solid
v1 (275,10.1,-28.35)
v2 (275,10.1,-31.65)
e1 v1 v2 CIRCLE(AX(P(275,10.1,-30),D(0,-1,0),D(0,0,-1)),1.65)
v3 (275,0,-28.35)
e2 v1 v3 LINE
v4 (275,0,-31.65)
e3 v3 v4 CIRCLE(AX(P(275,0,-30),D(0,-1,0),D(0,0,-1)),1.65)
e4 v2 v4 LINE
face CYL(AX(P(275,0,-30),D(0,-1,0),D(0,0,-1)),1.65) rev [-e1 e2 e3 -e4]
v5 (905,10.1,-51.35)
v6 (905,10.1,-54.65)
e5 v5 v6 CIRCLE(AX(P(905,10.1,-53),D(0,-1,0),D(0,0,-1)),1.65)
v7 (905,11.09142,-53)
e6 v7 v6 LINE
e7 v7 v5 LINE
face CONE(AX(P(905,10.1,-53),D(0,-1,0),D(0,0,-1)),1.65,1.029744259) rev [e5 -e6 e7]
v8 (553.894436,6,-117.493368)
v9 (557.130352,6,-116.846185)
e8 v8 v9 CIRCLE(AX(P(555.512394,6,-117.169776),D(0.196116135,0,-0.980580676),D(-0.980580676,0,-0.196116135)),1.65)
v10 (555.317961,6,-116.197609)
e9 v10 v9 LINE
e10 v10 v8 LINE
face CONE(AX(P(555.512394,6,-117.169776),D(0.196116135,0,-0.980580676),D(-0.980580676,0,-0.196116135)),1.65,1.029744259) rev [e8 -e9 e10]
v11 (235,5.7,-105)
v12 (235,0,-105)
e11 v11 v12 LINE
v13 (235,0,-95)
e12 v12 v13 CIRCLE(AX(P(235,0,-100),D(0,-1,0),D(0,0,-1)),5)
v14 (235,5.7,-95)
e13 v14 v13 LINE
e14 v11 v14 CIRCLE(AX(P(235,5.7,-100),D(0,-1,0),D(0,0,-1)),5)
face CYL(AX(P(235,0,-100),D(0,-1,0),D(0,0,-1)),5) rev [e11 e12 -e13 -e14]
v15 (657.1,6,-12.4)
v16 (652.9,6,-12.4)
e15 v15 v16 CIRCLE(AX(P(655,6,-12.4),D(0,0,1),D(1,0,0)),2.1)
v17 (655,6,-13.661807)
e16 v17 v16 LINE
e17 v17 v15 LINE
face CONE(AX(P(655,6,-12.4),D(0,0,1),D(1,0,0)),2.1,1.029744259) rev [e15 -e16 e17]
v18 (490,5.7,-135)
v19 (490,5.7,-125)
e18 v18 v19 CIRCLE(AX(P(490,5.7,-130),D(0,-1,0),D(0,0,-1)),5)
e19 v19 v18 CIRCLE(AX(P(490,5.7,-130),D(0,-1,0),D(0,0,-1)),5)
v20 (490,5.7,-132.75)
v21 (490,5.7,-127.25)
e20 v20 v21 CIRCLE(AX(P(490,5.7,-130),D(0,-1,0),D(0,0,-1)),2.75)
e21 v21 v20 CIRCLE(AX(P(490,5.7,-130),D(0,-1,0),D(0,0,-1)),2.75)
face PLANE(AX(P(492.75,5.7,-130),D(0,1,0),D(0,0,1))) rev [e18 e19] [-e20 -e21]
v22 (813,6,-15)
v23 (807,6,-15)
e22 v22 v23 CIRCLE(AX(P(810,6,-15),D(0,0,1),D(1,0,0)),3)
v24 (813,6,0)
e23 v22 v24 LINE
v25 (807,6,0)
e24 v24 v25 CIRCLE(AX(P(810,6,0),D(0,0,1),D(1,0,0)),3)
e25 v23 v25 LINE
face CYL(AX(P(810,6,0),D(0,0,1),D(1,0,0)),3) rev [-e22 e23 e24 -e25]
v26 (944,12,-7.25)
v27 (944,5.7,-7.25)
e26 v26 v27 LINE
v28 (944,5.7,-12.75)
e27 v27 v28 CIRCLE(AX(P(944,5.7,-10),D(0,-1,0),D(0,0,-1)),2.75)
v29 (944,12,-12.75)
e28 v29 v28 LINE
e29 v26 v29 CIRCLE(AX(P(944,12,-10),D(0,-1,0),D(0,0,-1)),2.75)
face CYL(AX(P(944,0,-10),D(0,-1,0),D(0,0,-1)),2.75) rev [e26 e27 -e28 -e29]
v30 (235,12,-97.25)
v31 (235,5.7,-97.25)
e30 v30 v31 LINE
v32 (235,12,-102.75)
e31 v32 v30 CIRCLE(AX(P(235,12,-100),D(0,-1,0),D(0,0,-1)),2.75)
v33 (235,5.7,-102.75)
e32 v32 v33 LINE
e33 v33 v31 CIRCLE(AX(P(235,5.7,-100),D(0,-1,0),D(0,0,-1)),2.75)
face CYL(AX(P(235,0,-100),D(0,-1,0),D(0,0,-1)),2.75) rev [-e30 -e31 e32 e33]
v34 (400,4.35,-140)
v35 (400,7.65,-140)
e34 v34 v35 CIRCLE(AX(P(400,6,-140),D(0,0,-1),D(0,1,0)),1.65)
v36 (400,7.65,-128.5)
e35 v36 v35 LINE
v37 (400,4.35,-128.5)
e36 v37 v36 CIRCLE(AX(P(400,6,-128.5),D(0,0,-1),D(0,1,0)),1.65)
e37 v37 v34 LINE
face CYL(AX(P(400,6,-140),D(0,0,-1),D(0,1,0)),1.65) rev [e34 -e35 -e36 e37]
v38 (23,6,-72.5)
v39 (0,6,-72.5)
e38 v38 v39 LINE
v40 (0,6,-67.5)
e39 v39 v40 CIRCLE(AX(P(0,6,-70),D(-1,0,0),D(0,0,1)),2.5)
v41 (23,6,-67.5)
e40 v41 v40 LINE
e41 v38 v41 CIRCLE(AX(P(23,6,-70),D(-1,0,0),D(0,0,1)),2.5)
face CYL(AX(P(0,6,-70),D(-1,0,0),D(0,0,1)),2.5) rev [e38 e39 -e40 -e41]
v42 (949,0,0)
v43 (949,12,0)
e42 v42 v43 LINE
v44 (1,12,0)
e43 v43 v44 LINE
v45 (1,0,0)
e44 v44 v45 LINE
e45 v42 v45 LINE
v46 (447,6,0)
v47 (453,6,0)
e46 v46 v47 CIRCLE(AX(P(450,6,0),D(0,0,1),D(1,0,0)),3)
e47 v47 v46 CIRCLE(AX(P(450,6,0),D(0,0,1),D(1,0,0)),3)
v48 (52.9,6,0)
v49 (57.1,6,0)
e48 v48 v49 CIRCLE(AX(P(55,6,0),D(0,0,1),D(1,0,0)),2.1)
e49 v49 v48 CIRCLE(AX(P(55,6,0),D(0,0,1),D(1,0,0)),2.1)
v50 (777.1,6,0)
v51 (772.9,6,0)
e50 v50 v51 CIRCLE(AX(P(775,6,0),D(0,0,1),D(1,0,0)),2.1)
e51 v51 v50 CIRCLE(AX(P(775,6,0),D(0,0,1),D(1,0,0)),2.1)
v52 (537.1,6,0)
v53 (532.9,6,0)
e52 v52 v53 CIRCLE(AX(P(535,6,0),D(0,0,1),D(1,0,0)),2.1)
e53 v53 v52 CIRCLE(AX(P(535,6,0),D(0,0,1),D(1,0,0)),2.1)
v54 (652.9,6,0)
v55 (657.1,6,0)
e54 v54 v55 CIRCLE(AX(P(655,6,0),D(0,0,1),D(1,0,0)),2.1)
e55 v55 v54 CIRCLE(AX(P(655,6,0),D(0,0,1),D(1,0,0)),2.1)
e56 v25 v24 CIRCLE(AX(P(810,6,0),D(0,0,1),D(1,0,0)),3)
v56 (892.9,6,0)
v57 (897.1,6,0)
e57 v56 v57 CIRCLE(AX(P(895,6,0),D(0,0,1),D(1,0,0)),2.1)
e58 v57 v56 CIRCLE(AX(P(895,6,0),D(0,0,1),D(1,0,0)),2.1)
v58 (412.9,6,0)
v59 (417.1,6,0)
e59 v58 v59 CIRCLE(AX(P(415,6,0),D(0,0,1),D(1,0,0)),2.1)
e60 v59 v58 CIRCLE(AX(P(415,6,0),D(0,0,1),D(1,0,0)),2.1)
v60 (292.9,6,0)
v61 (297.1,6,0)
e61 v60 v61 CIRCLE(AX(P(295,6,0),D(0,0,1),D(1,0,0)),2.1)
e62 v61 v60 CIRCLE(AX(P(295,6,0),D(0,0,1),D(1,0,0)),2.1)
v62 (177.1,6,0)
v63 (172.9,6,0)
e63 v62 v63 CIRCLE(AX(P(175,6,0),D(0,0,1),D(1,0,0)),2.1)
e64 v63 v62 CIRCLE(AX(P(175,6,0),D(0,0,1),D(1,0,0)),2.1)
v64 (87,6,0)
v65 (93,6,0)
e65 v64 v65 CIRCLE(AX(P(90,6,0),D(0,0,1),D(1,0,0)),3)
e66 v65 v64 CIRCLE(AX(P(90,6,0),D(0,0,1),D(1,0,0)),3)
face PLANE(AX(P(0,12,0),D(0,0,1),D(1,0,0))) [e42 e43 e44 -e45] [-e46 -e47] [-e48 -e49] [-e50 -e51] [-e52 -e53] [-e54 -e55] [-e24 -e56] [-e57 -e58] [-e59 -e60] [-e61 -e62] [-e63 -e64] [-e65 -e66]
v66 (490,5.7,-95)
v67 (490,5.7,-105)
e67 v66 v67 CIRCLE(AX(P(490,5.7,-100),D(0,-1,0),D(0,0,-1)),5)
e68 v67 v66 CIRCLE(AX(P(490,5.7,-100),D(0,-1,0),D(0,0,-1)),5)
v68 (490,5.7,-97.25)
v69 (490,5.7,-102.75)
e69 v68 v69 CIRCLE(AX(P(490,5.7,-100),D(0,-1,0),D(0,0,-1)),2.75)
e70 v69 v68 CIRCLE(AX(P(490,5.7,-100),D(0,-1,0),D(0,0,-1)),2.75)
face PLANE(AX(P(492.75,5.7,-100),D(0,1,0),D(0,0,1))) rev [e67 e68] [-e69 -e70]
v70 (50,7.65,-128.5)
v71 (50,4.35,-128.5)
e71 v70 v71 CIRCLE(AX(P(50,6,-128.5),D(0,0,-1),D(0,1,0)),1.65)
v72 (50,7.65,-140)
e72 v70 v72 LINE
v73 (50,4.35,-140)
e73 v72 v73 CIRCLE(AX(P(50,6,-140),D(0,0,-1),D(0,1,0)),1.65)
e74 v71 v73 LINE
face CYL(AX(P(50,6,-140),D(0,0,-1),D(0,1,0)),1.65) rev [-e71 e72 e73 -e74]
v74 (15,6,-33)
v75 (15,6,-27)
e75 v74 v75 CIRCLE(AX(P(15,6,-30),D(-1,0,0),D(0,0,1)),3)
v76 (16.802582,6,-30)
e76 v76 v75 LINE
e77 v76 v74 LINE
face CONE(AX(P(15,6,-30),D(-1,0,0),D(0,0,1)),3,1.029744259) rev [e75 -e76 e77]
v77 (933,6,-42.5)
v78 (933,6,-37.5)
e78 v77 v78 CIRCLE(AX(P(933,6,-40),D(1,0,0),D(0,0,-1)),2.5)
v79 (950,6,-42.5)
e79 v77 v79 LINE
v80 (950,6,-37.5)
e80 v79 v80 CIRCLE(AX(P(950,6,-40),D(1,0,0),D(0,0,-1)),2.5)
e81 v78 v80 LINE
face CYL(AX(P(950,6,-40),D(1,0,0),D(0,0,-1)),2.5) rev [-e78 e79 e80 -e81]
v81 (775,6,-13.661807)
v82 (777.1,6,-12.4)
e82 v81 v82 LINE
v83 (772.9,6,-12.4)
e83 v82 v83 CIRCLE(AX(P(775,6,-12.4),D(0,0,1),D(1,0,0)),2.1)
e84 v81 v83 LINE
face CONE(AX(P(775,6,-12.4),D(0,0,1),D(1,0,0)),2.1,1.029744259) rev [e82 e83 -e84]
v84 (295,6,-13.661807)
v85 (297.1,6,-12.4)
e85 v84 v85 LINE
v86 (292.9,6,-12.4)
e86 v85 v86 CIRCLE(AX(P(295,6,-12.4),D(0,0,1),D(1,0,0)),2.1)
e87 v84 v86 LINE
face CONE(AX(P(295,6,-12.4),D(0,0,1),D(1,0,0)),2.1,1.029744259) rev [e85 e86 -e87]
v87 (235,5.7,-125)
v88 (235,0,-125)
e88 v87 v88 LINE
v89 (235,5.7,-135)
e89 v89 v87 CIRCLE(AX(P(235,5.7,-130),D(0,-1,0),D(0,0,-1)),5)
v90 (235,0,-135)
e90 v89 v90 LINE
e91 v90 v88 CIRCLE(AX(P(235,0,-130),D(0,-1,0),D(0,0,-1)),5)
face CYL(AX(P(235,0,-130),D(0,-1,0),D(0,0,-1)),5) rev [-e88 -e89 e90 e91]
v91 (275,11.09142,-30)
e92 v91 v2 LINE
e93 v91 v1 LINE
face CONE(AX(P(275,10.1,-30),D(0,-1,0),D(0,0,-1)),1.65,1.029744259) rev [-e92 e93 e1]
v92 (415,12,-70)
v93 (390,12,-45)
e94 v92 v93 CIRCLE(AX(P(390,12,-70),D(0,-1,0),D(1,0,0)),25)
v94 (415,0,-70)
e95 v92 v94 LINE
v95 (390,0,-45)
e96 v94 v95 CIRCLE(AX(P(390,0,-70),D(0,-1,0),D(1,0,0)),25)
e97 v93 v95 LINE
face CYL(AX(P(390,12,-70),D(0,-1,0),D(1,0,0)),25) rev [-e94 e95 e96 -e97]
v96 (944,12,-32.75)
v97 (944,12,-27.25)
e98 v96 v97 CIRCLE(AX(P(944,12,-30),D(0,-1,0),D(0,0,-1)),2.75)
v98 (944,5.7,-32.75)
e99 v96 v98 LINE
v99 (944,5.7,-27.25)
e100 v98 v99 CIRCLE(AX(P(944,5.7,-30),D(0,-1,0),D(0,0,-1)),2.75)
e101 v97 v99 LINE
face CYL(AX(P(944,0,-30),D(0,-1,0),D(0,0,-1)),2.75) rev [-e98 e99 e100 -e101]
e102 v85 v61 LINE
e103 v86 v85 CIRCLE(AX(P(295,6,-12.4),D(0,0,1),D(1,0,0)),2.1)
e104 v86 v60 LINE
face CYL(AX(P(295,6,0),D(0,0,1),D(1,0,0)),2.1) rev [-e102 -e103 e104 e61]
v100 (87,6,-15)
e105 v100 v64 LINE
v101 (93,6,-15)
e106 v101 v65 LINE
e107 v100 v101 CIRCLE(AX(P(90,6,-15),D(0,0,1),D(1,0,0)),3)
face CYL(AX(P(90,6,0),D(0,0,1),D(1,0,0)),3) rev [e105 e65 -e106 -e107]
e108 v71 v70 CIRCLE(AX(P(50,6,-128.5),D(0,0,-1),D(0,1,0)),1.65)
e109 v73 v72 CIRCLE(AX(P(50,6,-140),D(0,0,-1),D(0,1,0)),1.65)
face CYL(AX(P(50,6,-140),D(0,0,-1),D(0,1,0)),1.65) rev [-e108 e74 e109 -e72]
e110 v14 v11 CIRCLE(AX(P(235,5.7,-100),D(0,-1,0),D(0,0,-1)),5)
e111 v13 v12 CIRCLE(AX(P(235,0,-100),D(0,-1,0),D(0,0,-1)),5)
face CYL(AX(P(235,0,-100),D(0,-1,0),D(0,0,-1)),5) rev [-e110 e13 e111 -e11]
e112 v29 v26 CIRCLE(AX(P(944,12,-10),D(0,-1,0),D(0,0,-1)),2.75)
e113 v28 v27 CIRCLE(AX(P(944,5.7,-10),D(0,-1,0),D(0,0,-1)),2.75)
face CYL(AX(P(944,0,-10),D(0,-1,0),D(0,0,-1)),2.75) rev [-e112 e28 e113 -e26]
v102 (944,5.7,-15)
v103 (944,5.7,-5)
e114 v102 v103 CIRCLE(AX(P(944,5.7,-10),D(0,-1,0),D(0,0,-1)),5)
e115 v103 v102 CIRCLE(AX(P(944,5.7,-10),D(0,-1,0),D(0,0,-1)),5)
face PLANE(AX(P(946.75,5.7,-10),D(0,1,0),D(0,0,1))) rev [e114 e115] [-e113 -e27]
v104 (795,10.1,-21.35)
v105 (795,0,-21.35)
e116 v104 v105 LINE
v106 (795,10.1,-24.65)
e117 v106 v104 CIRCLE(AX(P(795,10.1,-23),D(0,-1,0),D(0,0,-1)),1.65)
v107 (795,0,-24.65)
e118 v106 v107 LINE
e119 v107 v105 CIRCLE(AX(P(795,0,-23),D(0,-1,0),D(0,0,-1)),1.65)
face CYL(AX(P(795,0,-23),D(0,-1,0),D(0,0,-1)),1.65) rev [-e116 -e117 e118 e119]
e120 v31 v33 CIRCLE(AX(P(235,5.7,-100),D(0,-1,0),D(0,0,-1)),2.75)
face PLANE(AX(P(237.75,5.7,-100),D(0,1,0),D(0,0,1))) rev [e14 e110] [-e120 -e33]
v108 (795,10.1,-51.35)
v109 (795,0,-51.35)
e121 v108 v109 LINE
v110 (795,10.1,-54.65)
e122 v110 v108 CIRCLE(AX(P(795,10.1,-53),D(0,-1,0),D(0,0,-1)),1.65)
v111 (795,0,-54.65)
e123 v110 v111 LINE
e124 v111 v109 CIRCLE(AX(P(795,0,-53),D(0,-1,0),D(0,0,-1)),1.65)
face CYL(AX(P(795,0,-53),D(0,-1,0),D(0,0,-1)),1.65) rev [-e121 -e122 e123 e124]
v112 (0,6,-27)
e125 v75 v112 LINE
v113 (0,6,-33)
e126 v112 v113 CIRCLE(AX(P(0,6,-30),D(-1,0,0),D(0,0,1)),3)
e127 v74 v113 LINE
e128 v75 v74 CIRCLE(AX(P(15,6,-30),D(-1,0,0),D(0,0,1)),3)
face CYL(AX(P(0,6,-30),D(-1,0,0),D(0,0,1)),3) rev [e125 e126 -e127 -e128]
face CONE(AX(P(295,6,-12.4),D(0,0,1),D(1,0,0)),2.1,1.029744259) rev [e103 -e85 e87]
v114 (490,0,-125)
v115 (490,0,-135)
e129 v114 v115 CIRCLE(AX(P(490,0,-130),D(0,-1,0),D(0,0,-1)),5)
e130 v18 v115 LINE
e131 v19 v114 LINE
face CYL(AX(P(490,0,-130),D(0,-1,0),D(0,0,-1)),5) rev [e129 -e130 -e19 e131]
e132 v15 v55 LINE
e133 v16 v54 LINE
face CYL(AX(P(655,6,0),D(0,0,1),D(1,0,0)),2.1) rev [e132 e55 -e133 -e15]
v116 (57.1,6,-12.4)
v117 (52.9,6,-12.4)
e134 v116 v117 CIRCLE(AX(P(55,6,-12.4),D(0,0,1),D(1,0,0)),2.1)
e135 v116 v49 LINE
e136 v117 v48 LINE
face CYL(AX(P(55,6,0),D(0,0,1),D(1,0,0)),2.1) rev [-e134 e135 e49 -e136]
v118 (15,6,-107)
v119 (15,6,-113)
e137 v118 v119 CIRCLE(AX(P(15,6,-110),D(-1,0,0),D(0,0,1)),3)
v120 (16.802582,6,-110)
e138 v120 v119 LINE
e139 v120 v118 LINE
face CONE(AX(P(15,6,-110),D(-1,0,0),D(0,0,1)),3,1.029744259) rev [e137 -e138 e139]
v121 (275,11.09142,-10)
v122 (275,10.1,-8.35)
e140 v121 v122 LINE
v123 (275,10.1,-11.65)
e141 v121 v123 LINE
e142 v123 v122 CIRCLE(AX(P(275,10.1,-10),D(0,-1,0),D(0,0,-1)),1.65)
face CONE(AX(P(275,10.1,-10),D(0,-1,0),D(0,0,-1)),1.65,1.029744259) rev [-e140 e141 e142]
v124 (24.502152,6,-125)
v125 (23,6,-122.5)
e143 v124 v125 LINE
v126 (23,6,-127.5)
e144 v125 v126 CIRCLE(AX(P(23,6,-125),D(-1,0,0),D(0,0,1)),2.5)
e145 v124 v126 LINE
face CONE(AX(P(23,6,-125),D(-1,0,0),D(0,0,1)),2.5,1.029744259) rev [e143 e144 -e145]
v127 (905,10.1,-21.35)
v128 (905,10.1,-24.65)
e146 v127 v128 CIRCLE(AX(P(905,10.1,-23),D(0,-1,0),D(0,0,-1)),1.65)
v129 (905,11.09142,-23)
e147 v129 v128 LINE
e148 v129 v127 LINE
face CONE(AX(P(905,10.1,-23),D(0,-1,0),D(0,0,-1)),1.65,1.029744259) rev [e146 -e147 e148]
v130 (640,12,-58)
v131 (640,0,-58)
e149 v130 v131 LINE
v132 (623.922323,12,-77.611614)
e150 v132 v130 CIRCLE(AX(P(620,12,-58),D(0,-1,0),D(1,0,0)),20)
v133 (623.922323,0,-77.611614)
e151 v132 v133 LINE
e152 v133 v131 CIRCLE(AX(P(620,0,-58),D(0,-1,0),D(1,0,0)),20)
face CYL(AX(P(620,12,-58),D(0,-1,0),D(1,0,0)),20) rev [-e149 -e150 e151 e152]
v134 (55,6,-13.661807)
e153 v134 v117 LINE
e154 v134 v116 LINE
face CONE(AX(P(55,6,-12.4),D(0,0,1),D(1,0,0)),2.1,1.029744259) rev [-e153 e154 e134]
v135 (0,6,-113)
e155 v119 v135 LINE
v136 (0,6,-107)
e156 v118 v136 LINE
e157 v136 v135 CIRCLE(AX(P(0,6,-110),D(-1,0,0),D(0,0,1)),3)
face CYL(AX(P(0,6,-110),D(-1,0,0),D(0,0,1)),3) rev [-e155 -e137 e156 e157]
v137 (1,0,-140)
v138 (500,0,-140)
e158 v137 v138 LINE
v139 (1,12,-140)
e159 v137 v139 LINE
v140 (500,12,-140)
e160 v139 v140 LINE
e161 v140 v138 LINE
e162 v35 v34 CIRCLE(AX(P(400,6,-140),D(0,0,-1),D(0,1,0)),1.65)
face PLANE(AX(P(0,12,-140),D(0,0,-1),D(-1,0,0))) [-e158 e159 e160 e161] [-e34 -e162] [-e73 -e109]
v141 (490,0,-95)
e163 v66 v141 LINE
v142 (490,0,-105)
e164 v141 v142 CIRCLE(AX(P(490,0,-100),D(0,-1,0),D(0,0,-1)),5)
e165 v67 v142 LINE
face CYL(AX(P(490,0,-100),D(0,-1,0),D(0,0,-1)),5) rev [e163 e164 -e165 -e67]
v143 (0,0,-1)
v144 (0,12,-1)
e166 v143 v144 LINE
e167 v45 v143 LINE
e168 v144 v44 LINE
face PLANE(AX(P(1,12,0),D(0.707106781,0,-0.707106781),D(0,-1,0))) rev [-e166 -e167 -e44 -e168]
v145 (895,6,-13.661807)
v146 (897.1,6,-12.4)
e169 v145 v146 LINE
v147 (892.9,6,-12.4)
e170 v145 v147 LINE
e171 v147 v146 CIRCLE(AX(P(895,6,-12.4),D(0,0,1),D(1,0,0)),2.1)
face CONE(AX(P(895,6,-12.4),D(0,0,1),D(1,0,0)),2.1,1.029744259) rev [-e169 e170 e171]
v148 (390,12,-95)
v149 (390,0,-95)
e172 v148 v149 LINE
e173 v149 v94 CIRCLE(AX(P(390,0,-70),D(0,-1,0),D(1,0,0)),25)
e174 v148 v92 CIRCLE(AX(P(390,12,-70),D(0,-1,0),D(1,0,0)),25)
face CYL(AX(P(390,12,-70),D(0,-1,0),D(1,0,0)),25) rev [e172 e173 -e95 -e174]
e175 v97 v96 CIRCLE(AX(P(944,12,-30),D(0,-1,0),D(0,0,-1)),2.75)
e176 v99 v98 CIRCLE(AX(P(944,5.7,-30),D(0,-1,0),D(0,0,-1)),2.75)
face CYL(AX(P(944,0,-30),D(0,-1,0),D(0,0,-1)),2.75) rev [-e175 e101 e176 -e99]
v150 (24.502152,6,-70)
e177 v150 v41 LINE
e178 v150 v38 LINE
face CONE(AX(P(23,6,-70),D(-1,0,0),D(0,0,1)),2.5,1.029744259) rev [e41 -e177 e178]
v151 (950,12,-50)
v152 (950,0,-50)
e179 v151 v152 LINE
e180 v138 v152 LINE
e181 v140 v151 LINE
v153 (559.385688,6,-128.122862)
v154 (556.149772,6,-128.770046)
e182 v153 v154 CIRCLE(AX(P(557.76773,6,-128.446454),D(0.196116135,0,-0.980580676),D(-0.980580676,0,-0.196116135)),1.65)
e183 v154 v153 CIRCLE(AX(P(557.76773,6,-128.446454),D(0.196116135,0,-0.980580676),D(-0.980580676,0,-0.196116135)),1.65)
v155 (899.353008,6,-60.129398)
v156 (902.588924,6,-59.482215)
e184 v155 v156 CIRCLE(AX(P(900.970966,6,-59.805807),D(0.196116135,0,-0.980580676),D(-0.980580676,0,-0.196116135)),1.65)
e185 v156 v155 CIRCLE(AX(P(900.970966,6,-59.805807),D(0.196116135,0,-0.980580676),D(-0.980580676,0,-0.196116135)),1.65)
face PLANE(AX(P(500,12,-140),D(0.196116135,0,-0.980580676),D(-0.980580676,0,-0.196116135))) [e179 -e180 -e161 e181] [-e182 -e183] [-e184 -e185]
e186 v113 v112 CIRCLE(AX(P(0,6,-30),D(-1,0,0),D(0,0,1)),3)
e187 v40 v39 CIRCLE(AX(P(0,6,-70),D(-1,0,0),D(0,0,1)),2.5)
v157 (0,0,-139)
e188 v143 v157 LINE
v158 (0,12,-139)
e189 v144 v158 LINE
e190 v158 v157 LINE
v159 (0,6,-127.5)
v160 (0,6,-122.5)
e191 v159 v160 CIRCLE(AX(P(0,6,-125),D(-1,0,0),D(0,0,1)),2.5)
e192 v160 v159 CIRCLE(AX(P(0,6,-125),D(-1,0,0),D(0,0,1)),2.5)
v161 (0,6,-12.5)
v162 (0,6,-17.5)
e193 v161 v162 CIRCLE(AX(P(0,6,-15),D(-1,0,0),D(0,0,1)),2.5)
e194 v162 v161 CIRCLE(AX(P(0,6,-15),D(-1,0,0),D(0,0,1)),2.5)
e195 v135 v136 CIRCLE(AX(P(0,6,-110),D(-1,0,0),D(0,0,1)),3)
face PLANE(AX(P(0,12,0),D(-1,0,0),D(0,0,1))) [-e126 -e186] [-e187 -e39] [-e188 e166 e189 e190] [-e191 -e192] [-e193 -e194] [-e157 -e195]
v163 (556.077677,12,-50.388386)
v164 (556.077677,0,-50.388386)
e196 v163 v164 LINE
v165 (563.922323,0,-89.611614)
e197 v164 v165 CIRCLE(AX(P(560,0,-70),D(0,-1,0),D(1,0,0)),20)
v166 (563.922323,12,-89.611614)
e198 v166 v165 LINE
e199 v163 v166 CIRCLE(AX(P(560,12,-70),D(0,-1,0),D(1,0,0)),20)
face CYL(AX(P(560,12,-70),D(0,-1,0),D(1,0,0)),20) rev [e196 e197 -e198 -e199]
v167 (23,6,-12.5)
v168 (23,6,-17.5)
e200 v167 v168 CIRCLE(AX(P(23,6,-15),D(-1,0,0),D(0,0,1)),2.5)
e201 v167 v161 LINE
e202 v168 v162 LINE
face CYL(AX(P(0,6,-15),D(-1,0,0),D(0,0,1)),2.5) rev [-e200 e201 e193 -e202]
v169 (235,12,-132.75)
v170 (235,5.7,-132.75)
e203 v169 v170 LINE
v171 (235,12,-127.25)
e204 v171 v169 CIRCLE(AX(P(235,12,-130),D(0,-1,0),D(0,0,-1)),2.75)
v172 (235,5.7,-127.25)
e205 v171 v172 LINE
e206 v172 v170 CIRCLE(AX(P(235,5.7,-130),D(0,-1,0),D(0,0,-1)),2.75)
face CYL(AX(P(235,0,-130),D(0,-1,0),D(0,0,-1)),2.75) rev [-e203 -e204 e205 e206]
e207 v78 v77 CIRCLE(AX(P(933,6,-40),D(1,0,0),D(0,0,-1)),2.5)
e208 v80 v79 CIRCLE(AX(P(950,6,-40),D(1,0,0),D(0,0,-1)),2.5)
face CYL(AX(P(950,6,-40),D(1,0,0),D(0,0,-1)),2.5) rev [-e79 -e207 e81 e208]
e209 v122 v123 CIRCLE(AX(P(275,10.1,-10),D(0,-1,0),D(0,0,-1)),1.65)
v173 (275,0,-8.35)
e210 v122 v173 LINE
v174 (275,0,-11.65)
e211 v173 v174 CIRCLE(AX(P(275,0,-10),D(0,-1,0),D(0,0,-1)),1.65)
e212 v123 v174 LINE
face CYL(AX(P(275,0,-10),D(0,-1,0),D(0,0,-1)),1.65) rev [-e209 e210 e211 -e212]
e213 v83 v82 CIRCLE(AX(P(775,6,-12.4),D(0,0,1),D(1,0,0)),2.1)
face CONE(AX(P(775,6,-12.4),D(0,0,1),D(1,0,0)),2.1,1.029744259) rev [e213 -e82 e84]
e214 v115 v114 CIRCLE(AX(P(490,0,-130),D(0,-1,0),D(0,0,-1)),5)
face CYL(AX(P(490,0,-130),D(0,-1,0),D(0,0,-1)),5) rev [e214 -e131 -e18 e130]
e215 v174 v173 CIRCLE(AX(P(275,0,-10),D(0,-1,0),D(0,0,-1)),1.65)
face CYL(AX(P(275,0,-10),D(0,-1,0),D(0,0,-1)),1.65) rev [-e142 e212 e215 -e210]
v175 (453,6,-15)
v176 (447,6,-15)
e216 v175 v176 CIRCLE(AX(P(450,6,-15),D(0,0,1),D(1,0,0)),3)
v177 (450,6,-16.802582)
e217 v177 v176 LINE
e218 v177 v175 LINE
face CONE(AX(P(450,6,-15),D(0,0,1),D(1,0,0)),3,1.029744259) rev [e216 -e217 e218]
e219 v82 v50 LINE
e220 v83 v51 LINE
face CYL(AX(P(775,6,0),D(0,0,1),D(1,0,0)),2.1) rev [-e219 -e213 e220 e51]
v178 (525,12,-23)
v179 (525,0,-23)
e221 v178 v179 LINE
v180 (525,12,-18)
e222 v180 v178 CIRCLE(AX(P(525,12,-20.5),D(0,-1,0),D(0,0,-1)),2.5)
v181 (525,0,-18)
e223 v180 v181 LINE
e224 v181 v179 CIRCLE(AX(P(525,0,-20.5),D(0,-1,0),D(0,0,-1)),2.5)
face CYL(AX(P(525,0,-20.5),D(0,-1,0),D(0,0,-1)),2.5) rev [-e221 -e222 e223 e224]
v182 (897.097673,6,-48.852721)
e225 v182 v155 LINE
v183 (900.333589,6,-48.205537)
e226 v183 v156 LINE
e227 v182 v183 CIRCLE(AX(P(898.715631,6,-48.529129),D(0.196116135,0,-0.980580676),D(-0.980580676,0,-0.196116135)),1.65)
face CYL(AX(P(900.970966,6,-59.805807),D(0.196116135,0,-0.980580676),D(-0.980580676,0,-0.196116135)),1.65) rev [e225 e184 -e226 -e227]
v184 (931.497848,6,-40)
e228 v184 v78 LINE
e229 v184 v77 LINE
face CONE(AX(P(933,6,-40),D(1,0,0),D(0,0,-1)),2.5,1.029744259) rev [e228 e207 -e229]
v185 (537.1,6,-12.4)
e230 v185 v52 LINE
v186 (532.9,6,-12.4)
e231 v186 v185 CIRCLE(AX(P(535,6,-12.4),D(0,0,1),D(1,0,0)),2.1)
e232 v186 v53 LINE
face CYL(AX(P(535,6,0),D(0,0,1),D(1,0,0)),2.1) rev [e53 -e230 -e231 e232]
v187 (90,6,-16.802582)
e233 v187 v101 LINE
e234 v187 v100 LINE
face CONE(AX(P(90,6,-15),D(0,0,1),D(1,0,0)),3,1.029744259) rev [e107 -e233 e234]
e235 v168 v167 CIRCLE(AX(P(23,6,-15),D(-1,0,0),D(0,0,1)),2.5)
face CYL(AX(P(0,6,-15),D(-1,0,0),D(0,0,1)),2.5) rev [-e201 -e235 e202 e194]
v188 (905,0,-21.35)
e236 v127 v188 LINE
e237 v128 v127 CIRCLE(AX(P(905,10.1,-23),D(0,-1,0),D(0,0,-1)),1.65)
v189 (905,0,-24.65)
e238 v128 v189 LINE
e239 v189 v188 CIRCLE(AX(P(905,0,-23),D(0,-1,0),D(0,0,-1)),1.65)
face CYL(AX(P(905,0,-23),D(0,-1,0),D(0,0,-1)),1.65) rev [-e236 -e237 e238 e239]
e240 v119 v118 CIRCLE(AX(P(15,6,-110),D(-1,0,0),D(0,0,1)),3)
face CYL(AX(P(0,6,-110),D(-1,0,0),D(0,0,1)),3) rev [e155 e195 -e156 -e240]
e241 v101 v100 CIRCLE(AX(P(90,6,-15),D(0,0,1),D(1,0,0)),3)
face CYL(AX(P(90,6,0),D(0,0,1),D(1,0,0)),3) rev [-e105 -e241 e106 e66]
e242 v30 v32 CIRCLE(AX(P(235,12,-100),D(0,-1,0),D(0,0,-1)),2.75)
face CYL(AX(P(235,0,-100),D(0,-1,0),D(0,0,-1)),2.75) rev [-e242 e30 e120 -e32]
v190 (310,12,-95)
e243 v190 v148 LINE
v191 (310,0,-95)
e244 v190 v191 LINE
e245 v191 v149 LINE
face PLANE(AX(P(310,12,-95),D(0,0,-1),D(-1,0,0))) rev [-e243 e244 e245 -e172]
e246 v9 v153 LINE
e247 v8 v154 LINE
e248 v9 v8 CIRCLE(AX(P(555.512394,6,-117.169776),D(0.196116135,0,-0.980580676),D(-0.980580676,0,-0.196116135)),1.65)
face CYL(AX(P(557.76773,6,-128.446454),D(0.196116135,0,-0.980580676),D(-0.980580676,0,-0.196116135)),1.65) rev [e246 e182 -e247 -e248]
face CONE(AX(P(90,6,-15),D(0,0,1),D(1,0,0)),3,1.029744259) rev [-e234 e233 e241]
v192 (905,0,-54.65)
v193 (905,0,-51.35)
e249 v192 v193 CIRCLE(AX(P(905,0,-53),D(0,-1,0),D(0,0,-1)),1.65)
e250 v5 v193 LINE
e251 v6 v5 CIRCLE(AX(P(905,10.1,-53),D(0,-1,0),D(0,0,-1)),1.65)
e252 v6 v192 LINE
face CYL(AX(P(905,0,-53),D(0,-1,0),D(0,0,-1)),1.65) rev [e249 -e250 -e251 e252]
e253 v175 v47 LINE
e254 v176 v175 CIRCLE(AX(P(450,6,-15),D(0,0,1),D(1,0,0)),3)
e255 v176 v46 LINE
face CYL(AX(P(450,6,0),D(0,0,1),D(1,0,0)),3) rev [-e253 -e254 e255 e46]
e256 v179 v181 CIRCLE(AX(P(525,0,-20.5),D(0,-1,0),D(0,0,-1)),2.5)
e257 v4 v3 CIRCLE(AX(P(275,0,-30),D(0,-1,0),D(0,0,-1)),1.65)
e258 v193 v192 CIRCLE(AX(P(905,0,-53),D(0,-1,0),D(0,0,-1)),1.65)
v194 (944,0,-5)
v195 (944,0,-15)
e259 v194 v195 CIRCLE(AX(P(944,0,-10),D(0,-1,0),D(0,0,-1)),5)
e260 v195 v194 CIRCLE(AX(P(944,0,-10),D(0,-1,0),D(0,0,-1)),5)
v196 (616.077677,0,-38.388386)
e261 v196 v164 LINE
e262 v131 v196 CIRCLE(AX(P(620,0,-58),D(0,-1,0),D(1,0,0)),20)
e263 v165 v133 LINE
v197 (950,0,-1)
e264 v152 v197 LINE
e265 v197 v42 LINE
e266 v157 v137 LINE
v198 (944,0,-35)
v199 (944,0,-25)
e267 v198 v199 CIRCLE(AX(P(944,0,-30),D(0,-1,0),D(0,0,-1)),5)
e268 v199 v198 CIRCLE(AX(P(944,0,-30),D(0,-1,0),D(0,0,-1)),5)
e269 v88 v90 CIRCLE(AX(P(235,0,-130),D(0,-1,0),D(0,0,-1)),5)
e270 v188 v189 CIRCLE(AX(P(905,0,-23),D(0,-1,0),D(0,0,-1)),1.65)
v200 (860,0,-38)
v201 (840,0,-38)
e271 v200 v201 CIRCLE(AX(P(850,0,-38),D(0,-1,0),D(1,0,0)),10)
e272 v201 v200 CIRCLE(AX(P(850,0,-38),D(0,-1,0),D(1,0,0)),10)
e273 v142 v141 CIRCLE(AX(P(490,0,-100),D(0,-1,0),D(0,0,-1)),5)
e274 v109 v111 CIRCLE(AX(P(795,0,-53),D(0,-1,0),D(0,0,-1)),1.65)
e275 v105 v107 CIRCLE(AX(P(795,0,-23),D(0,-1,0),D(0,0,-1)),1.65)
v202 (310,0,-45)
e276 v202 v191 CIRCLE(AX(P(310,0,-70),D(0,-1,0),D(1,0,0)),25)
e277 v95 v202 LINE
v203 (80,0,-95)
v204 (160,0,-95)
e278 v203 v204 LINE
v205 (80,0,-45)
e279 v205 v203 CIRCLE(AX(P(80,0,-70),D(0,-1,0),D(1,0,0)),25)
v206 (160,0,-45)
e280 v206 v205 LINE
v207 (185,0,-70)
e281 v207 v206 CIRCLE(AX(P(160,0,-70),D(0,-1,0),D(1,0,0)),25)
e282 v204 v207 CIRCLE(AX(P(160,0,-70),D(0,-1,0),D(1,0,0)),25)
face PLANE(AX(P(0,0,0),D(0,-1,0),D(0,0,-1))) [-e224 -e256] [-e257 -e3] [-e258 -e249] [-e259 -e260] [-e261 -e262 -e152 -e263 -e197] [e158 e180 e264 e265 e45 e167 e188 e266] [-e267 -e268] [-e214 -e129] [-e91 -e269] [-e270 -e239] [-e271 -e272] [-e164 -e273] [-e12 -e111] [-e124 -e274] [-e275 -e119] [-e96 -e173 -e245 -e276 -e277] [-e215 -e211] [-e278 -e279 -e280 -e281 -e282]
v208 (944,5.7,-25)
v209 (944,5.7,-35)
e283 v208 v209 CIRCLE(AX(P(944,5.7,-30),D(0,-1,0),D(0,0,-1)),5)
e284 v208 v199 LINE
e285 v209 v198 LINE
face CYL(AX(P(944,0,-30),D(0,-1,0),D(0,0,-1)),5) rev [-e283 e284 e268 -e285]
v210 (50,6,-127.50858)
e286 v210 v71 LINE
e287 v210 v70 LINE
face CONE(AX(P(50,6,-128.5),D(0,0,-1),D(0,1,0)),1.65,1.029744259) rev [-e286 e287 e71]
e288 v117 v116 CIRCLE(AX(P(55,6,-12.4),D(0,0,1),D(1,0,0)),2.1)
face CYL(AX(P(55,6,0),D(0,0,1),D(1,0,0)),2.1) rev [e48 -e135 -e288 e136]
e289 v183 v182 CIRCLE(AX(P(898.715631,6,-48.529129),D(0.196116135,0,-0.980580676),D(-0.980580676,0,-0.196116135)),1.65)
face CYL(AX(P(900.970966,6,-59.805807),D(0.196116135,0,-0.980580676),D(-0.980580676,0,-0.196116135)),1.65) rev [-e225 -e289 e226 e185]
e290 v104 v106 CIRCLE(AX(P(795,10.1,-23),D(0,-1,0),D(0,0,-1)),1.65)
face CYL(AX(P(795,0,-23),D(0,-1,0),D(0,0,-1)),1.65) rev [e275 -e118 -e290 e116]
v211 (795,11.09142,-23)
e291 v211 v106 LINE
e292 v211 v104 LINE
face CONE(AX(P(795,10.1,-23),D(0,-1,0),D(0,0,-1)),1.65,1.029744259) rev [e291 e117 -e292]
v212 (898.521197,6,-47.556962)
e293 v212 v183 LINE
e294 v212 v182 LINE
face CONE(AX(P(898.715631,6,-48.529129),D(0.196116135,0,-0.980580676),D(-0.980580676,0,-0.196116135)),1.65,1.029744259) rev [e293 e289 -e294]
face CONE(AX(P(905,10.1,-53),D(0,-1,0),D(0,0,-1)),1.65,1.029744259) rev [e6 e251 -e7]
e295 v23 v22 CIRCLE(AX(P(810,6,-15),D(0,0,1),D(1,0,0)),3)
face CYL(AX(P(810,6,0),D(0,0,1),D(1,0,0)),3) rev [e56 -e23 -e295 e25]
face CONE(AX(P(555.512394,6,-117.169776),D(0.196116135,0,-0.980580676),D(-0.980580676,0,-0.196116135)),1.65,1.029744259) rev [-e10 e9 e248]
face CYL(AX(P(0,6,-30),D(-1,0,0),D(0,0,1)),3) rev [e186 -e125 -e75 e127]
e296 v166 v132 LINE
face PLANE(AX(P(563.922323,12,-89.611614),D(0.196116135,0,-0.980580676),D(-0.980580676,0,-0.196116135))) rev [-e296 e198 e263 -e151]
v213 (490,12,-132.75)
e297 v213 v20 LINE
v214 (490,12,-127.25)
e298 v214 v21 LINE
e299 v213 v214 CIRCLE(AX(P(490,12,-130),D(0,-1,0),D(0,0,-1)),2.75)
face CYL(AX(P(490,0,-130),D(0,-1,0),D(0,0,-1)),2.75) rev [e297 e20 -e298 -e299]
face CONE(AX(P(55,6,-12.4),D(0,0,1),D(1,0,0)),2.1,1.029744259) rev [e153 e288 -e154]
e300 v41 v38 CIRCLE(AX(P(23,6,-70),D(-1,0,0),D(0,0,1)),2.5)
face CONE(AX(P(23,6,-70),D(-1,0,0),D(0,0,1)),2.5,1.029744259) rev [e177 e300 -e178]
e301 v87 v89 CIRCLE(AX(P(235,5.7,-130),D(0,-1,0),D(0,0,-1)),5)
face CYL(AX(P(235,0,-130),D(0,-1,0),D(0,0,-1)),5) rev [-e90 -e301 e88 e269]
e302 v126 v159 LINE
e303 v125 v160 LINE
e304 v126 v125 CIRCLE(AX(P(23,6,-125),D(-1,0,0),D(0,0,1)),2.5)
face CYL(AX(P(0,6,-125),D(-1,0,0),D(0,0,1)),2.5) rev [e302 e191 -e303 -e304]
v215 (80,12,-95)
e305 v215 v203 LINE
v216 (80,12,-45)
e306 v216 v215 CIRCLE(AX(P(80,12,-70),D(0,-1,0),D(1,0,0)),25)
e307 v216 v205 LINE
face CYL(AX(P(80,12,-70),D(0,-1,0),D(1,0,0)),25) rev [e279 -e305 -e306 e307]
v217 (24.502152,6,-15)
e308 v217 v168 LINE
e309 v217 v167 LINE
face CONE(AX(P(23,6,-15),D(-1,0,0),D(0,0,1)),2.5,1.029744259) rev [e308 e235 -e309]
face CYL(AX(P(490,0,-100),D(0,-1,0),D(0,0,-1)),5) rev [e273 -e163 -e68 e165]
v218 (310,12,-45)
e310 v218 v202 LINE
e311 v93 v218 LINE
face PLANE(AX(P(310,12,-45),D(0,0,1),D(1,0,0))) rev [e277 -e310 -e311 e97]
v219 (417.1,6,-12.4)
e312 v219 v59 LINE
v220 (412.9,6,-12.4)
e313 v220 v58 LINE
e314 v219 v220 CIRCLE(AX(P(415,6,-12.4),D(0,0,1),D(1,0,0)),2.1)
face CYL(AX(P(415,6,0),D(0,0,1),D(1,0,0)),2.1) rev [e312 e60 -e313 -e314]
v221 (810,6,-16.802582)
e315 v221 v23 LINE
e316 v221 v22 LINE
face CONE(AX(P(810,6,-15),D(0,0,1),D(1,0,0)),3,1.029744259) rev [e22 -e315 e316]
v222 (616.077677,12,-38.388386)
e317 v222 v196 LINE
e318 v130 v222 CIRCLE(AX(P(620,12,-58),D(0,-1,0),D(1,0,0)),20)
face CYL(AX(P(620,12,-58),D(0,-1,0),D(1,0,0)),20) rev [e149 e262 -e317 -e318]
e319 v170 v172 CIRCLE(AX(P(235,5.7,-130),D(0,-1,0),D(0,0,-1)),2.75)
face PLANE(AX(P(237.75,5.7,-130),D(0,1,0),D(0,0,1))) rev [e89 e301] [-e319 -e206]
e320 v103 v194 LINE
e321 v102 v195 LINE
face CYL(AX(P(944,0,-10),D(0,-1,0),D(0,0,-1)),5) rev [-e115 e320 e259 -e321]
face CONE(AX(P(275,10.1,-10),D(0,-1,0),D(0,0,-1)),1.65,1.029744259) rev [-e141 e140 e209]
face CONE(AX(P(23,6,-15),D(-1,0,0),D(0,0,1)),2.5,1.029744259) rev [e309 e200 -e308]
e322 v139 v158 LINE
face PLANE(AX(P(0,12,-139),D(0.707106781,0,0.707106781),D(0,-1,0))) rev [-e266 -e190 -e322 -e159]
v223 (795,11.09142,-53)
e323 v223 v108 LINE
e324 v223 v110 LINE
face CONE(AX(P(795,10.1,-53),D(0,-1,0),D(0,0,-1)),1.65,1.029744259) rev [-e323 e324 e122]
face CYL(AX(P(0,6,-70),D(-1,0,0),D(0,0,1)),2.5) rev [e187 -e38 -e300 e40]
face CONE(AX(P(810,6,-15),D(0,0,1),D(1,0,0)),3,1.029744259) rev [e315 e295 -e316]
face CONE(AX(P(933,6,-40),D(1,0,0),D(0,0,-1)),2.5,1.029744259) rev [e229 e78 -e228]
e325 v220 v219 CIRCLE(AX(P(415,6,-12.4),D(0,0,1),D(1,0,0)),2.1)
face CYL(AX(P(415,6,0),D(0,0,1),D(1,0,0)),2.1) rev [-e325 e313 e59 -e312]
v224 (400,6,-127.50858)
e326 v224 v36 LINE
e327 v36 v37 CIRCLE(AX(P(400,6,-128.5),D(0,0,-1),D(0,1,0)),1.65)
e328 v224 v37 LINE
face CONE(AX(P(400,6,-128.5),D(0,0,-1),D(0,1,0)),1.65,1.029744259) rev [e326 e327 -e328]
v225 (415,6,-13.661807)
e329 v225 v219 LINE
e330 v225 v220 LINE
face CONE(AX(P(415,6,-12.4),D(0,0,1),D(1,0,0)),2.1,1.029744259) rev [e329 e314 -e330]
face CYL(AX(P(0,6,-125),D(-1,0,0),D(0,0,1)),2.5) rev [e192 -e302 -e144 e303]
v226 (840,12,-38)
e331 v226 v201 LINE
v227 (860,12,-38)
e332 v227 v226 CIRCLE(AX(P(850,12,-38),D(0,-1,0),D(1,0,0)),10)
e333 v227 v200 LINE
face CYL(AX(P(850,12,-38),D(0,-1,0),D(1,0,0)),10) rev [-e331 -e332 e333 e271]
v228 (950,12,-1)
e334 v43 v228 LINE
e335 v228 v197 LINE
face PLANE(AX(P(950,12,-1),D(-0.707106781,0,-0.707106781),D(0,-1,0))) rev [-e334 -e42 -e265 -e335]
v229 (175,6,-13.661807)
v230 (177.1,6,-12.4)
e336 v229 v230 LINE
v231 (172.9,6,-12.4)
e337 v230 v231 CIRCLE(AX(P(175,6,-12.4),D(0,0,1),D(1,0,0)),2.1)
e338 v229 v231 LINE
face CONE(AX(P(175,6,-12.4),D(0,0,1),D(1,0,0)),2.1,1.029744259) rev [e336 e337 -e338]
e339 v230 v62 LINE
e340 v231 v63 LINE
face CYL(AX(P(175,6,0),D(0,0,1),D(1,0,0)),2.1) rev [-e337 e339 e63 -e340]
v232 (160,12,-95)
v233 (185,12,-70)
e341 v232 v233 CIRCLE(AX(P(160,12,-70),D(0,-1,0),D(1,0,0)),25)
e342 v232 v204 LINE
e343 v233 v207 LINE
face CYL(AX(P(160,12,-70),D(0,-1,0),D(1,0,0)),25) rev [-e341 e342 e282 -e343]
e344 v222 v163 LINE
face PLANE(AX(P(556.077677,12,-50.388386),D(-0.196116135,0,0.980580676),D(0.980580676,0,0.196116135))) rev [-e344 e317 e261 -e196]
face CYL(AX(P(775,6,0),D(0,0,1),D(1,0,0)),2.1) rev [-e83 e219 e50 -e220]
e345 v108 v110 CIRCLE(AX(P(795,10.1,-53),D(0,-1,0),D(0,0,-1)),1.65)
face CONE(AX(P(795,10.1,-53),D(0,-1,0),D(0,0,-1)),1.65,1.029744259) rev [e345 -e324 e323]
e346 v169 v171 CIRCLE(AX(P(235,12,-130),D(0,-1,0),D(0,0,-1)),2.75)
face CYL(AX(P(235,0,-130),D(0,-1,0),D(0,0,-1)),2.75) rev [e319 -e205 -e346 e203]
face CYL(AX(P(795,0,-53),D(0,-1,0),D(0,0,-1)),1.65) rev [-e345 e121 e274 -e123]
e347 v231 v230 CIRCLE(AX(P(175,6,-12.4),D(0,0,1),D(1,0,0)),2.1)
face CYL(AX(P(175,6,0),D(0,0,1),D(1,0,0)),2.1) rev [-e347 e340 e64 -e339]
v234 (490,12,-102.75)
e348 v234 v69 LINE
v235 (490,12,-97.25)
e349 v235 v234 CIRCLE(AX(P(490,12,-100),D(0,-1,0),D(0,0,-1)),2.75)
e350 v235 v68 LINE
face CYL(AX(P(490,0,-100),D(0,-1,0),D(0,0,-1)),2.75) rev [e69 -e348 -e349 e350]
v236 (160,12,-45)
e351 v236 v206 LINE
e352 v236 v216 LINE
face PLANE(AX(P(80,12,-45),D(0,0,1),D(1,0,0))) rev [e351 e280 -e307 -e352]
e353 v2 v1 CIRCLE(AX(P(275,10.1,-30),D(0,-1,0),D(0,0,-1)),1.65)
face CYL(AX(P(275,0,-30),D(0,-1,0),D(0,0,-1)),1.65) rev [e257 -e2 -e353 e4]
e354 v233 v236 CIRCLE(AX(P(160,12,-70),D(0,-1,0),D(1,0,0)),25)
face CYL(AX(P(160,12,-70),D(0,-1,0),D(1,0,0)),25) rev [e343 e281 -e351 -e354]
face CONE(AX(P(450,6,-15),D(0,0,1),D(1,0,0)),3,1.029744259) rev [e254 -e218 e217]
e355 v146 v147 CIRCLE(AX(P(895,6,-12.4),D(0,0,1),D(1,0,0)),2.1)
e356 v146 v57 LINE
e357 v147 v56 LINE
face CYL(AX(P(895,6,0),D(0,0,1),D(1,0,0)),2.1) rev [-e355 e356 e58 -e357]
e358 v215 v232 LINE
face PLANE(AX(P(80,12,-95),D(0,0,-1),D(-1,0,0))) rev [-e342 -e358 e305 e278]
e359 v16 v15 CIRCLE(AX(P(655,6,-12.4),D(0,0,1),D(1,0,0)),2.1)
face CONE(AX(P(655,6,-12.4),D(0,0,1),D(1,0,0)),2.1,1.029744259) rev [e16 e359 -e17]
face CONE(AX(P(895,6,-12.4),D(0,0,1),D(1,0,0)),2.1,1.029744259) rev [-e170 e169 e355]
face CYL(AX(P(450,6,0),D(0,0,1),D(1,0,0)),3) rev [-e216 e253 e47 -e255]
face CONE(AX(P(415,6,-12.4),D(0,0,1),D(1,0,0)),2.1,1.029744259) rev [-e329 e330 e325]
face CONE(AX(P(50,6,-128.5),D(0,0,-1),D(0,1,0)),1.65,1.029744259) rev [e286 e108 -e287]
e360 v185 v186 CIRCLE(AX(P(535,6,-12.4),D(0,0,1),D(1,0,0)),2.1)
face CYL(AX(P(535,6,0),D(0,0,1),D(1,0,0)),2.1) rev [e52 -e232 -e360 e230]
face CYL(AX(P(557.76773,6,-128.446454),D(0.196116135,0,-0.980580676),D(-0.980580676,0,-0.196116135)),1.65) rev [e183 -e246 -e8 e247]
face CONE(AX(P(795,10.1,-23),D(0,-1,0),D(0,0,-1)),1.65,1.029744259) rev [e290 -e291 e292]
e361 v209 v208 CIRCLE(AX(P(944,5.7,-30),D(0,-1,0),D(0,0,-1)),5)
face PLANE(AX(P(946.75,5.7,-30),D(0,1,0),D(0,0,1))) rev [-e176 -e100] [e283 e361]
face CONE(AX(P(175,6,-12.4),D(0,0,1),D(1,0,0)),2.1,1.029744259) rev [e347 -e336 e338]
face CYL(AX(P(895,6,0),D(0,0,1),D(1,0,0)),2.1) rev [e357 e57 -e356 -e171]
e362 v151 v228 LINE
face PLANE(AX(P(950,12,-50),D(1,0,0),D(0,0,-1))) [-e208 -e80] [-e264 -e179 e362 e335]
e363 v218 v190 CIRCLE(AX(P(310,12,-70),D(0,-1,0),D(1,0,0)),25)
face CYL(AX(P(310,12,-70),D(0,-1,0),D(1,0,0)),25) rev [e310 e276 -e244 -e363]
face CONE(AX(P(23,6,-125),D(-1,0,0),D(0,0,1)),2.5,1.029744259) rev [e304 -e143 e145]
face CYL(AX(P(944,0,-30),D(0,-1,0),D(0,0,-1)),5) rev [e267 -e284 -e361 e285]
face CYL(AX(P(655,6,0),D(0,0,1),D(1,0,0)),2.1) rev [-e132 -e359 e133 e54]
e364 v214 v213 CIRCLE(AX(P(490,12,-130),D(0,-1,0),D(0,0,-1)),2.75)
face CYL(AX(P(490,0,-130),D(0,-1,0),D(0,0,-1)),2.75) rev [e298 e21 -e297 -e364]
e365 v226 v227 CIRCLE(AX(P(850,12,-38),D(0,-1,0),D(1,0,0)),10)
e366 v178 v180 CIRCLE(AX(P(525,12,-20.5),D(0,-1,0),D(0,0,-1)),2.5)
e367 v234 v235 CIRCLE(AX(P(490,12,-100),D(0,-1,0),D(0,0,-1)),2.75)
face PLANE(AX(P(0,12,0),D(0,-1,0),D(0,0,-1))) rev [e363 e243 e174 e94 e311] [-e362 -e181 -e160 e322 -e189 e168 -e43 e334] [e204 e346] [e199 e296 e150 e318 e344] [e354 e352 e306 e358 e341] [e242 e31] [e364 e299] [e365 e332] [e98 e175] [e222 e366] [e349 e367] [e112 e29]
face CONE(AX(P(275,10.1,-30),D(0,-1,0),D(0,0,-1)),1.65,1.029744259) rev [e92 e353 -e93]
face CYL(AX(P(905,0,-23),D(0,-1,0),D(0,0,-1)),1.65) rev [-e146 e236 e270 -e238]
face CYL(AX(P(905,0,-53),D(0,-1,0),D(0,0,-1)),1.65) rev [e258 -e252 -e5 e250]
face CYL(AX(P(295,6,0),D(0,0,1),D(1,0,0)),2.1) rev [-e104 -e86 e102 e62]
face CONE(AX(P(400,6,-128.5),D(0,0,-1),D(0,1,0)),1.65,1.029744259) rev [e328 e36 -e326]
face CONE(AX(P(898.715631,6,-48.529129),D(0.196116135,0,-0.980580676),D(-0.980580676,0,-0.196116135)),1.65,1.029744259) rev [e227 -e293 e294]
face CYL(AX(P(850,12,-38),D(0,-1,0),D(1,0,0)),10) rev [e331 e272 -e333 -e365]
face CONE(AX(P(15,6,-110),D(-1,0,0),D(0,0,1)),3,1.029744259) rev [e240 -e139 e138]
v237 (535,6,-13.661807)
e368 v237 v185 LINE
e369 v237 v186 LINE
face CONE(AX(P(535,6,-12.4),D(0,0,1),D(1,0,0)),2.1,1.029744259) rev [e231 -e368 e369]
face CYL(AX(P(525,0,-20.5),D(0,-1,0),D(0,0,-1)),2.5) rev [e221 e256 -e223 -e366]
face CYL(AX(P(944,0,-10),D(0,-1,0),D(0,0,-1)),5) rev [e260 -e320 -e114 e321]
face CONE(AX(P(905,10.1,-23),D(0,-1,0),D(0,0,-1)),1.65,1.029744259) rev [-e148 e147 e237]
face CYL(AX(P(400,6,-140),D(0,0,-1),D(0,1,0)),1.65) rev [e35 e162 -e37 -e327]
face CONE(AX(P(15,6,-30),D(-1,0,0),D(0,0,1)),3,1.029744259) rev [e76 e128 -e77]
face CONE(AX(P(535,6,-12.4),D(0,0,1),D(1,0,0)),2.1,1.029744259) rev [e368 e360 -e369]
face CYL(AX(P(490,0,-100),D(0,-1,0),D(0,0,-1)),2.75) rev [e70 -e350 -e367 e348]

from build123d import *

# Parameters (mm, degrees)
BOSS_EXTRUDE2_DEPTH                              = 12
SKETCH9_R                                        = 10
CUT_EXTRUDE3_DEPTH                               = 12
M4_TAPPED_HOLE2_D                                = 3.3
M4_TAPPED_HOLE2_DEPTH                            = 10.1
M4_TAPPED_HOLE2_TIP                              = 0.991420021
M6_TAPPED_HOLE1_D                                = 5
M6_TAPPED_HOLE1_DEPTH                            = 15
M6_TAPPED_HOLE1_TIP                              = 1.502151548
M4_TAPPED_HOLE3_D                                = 3.3
M4_TAPPED_HOLE3_DEPTH                            = 11.5
M4_TAPPED_HOLE3_TIP                              = 0.991420021
M4_TAPPED_HOLE4_D                                = 3.3
M4_TAPPED_HOLE4_DEPTH                            = 11.5
M4_TAPPED_HOLE4_TIP                              = 0.991420021
M6_TAPPED_HOLE3_D                                = 5
M6_TAPPED_HOLE3_DEPTH                            = 17
M6_TAPPED_HOLE3_TIP                              = 1.502151548
M6_TAPPED_HOLE2_D                                = 5
M6_TAPPED_HOLE2_DEPTH                            = 23
M6_TAPPED_HOLE2_TIP                              = 1.502151548
F_6_0_6_DIAMETER_HOLE1_D                         = 6
F_6_0_6_DIAMETER_HOLE1_DEPTH                     = 15
F_6_0_6_DIAMETER_HOLE1_TIP                       = 1.802581857
M5_TAPPED_HOLE1_D                                = 4.2
M5_TAPPED_HOLE1_DEPTH                            = 12.4
M5_TAPPED_HOLE1_TIP                              = 1.2618073
F_6_0_6_DIAMETER_HOLE2_D                         = 6
F_6_0_6_DIAMETER_HOLE2_DEPTH                     = 15
F_6_0_6_DIAMETER_HOLE2_TIP                       = 1.802581857
HOLE_SIZE_PER_HEX_SOCKET_SCREW_TYPE1_D           = 5.5
HOLE_SIZE_PER_HEX_SOCKET_SCREW_TYPE1_CBORE_D     = 10
HOLE_SIZE_PER_HEX_SOCKET_SCREW_TYPE1_CBORE_DEPTH = 5.7
CHAMFER2_SIZE                                    = 1


with BuildPart() as part:
    # Sketch2 → Boss-Extrude2 (new body)
    with BuildSketch(Plane(origin=(0, 0, 0), x_dir=(-1, 0, 0), z_dir=(0, -1, 0))):
        Polygon((0, 0), (0, 140), (-500, 140), (-950, 50), (-950, 0), align=None)
    extrude(amount=-BOSS_EXTRUDE2_DEPTH)

    # Sketch9 → Cut-Extrude3 (cut)
    with BuildSketch(Plane.XZ):
        with Locations((850, -38)):
            Circle(SKETCH9_R)
        with BuildLine():
            Line((80, -45), (160, -45))
            ThreePointArc((160, -45), (185, -70), (160, -95))
            Line((160, -95), (80, -95))
            ThreePointArc((80, -95), (55, -70), (80, -45))
        make_face()
        with BuildLine():
            Line((310, -45), (390, -45))
            ThreePointArc((390, -45), (415, -70), (390, -95))
            Line((390, -95), (310, -95))
            ThreePointArc((310, -95), (285, -70), (310, -45))
        make_face()
        with BuildLine():
            Line((556.077677297, -50.388386486), (616.077677297, -38.388386486))
            ThreePointArc((616.077677297, -38.388386486), (639.611613514, -54.077677297), (623.922322703, -77.611613514))
            Line((623.922322703, -77.611613514), (563.922322703, -89.611613514))
            ThreePointArc((563.922322703, -89.611613514), (540.388386486, -73.922322703), (556.077677297, -50.388386486))
        make_face()
    extrude(amount=-CUT_EXTRUDE3_DEPTH, mode=Mode.SUBTRACT)

    # M4 Tapped Hole2
    with Locations(Plane(origin=(0, 0, 0), x_dir=(-1, 0, 0), z_dir=(0, -1, 0))):
        with Locations((-275, 10), (-275, 30), (-795, 23), (-905, 23), (-795, 53), (-905, 53)):
            Hole(M4_TAPPED_HOLE2_D / 2, depth=M4_TAPPED_HOLE2_DEPTH)
            with Locations((0, 0, -(M4_TAPPED_HOLE2_DEPTH + M4_TAPPED_HOLE2_TIP / 2))):  # 118° drill point
                Cone(0, M4_TAPPED_HOLE2_D / 2, M4_TAPPED_HOLE2_TIP, mode=Mode.SUBTRACT)

    # M6 Tapped Hole1
    with Locations(Plane(origin=(0, 0, 0), x_dir=(-1, 0, 0), z_dir=(0, -1, 0))):
        with Locations((-525, 20.5)):
            Hole(M6_TAPPED_HOLE1_D / 2, depth=M6_TAPPED_HOLE1_DEPTH)
            with Locations((0, 0, -(M6_TAPPED_HOLE1_DEPTH + M6_TAPPED_HOLE1_TIP / 2))):  # 118° drill point
                Cone(0, M6_TAPPED_HOLE1_D / 2, M6_TAPPED_HOLE1_TIP, mode=Mode.SUBTRACT)

    # M4 Tapped Hole3
    with Locations(Plane(origin=(0, 0, -140), x_dir=(-1, 0, 0), z_dir=(0, 0, -1))):
        with Locations((-50, 6), (-400, 6)):
            Hole(M4_TAPPED_HOLE3_D / 2, depth=M4_TAPPED_HOLE3_DEPTH)
            with Locations((0, 0, -(M4_TAPPED_HOLE3_DEPTH + M4_TAPPED_HOLE3_TIP / 2))):  # 118° drill point
                Cone(0, M4_TAPPED_HOLE3_D / 2, M4_TAPPED_HOLE3_TIP, mode=Mode.SUBTRACT)

    # M4 Tapped Hole4
    with Locations(Plane(origin=(46.153846154, 0, -230.769230769), x_dir=(-0.9805806756909201, 0, -0.19611613513818424), z_dir=(0.19611613513818424, 0, -0.9805806756909201))):
        with Locations((-871.745835149, 6), (-521.745835149, 6)):
            Hole(M4_TAPPED_HOLE4_D / 2, depth=M4_TAPPED_HOLE4_DEPTH)
            with Locations((0, 0, -(M4_TAPPED_HOLE4_DEPTH + M4_TAPPED_HOLE4_TIP / 2))):  # 118° drill point
                Cone(0, M4_TAPPED_HOLE4_D / 2, M4_TAPPED_HOLE4_TIP, mode=Mode.SUBTRACT)

    # M6 Tapped Hole3
    with Locations(Plane(origin=(950, 0, 0), x_dir=(0, 0, -1), z_dir=(1, 0, 0))):
        with Locations((40, 6), (40, 96)):
            Hole(M6_TAPPED_HOLE3_D / 2, depth=M6_TAPPED_HOLE3_DEPTH)
            with Locations((0, 0, -(M6_TAPPED_HOLE3_DEPTH + M6_TAPPED_HOLE3_TIP / 2))):  # 118° drill point
                Cone(0, M6_TAPPED_HOLE3_D / 2, M6_TAPPED_HOLE3_TIP, mode=Mode.SUBTRACT)

    # M6 Tapped Hole2
    with Locations(Plane.ZY):
        with Locations((-15, 6), (-70, 6), (-125, 6)):
            Hole(M6_TAPPED_HOLE2_D / 2, depth=M6_TAPPED_HOLE2_DEPTH)
            with Locations((0, 0, -(M6_TAPPED_HOLE2_DEPTH + M6_TAPPED_HOLE2_TIP / 2))):  # 118° drill point
                Cone(0, M6_TAPPED_HOLE2_D / 2, M6_TAPPED_HOLE2_TIP, mode=Mode.SUBTRACT)

    # Ø6.0 (6) Diameter Hole1
    with Locations(Plane.ZY):
        with Locations((-30, 6), (-110, 6)):
            Hole(F_6_0_6_DIAMETER_HOLE1_D / 2, depth=F_6_0_6_DIAMETER_HOLE1_DEPTH)
            with Locations((0, 0, -(F_6_0_6_DIAMETER_HOLE1_DEPTH + F_6_0_6_DIAMETER_HOLE1_TIP / 2))):  # 118° drill point
                Cone(0, F_6_0_6_DIAMETER_HOLE1_D / 2, F_6_0_6_DIAMETER_HOLE1_TIP, mode=Mode.SUBTRACT)

    # M5 Tapped Hole1
    with Locations(Plane.XY):
        with Locations((55, 6), (175, 6), (295, 6), (415, 6), (535, 6), (655, 6), (775, 6), (895, 6)):
            Hole(M5_TAPPED_HOLE1_D / 2, depth=M5_TAPPED_HOLE1_DEPTH)
            with Locations((0, 0, -(M5_TAPPED_HOLE1_DEPTH + M5_TAPPED_HOLE1_TIP / 2))):  # 118° drill point
                Cone(0, M5_TAPPED_HOLE1_D / 2, M5_TAPPED_HOLE1_TIP, mode=Mode.SUBTRACT)

    # Ø6.0 (6) Diameter Hole2
    with Locations(Plane.XY):
        with Locations((90, 6), (450, 6), (810, 6)):
            Hole(F_6_0_6_DIAMETER_HOLE2_D / 2, depth=F_6_0_6_DIAMETER_HOLE2_DEPTH)
            with Locations((0, 0, -(F_6_0_6_DIAMETER_HOLE2_DEPTH + F_6_0_6_DIAMETER_HOLE2_TIP / 2))):  # 118° drill point
                Cone(0, F_6_0_6_DIAMETER_HOLE2_D / 2, F_6_0_6_DIAMETER_HOLE2_TIP, mode=Mode.SUBTRACT)

    # Hole size per hex socket screw type1 (through all)
    with Locations(Plane(origin=(0, 0, 0), x_dir=(-1, 0, 0), z_dir=(0, -1, 0))):
        with Locations((-235, 100), (-235, 130), (-490, 100), (-490, 130), (-944, 10), (-944, 30)):
            CounterBoreHole(HOLE_SIZE_PER_HEX_SOCKET_SCREW_TYPE1_D / 2, HOLE_SIZE_PER_HEX_SOCKET_SCREW_TYPE1_CBORE_D / 2, HOLE_SIZE_PER_HEX_SOCKET_SCREW_TYPE1_CBORE_DEPTH)

    # Chamfer2
    chamfer2_edges = [part.edges().sort_by_distance(p)[0] for p in [
        (950, 6, 0),
        (0, 6, -140),
        (0, 6, 0),
    ]]
    chamfer(chamfer2_edges, length=CHAMFER2_SIZE)


solid = part.part
